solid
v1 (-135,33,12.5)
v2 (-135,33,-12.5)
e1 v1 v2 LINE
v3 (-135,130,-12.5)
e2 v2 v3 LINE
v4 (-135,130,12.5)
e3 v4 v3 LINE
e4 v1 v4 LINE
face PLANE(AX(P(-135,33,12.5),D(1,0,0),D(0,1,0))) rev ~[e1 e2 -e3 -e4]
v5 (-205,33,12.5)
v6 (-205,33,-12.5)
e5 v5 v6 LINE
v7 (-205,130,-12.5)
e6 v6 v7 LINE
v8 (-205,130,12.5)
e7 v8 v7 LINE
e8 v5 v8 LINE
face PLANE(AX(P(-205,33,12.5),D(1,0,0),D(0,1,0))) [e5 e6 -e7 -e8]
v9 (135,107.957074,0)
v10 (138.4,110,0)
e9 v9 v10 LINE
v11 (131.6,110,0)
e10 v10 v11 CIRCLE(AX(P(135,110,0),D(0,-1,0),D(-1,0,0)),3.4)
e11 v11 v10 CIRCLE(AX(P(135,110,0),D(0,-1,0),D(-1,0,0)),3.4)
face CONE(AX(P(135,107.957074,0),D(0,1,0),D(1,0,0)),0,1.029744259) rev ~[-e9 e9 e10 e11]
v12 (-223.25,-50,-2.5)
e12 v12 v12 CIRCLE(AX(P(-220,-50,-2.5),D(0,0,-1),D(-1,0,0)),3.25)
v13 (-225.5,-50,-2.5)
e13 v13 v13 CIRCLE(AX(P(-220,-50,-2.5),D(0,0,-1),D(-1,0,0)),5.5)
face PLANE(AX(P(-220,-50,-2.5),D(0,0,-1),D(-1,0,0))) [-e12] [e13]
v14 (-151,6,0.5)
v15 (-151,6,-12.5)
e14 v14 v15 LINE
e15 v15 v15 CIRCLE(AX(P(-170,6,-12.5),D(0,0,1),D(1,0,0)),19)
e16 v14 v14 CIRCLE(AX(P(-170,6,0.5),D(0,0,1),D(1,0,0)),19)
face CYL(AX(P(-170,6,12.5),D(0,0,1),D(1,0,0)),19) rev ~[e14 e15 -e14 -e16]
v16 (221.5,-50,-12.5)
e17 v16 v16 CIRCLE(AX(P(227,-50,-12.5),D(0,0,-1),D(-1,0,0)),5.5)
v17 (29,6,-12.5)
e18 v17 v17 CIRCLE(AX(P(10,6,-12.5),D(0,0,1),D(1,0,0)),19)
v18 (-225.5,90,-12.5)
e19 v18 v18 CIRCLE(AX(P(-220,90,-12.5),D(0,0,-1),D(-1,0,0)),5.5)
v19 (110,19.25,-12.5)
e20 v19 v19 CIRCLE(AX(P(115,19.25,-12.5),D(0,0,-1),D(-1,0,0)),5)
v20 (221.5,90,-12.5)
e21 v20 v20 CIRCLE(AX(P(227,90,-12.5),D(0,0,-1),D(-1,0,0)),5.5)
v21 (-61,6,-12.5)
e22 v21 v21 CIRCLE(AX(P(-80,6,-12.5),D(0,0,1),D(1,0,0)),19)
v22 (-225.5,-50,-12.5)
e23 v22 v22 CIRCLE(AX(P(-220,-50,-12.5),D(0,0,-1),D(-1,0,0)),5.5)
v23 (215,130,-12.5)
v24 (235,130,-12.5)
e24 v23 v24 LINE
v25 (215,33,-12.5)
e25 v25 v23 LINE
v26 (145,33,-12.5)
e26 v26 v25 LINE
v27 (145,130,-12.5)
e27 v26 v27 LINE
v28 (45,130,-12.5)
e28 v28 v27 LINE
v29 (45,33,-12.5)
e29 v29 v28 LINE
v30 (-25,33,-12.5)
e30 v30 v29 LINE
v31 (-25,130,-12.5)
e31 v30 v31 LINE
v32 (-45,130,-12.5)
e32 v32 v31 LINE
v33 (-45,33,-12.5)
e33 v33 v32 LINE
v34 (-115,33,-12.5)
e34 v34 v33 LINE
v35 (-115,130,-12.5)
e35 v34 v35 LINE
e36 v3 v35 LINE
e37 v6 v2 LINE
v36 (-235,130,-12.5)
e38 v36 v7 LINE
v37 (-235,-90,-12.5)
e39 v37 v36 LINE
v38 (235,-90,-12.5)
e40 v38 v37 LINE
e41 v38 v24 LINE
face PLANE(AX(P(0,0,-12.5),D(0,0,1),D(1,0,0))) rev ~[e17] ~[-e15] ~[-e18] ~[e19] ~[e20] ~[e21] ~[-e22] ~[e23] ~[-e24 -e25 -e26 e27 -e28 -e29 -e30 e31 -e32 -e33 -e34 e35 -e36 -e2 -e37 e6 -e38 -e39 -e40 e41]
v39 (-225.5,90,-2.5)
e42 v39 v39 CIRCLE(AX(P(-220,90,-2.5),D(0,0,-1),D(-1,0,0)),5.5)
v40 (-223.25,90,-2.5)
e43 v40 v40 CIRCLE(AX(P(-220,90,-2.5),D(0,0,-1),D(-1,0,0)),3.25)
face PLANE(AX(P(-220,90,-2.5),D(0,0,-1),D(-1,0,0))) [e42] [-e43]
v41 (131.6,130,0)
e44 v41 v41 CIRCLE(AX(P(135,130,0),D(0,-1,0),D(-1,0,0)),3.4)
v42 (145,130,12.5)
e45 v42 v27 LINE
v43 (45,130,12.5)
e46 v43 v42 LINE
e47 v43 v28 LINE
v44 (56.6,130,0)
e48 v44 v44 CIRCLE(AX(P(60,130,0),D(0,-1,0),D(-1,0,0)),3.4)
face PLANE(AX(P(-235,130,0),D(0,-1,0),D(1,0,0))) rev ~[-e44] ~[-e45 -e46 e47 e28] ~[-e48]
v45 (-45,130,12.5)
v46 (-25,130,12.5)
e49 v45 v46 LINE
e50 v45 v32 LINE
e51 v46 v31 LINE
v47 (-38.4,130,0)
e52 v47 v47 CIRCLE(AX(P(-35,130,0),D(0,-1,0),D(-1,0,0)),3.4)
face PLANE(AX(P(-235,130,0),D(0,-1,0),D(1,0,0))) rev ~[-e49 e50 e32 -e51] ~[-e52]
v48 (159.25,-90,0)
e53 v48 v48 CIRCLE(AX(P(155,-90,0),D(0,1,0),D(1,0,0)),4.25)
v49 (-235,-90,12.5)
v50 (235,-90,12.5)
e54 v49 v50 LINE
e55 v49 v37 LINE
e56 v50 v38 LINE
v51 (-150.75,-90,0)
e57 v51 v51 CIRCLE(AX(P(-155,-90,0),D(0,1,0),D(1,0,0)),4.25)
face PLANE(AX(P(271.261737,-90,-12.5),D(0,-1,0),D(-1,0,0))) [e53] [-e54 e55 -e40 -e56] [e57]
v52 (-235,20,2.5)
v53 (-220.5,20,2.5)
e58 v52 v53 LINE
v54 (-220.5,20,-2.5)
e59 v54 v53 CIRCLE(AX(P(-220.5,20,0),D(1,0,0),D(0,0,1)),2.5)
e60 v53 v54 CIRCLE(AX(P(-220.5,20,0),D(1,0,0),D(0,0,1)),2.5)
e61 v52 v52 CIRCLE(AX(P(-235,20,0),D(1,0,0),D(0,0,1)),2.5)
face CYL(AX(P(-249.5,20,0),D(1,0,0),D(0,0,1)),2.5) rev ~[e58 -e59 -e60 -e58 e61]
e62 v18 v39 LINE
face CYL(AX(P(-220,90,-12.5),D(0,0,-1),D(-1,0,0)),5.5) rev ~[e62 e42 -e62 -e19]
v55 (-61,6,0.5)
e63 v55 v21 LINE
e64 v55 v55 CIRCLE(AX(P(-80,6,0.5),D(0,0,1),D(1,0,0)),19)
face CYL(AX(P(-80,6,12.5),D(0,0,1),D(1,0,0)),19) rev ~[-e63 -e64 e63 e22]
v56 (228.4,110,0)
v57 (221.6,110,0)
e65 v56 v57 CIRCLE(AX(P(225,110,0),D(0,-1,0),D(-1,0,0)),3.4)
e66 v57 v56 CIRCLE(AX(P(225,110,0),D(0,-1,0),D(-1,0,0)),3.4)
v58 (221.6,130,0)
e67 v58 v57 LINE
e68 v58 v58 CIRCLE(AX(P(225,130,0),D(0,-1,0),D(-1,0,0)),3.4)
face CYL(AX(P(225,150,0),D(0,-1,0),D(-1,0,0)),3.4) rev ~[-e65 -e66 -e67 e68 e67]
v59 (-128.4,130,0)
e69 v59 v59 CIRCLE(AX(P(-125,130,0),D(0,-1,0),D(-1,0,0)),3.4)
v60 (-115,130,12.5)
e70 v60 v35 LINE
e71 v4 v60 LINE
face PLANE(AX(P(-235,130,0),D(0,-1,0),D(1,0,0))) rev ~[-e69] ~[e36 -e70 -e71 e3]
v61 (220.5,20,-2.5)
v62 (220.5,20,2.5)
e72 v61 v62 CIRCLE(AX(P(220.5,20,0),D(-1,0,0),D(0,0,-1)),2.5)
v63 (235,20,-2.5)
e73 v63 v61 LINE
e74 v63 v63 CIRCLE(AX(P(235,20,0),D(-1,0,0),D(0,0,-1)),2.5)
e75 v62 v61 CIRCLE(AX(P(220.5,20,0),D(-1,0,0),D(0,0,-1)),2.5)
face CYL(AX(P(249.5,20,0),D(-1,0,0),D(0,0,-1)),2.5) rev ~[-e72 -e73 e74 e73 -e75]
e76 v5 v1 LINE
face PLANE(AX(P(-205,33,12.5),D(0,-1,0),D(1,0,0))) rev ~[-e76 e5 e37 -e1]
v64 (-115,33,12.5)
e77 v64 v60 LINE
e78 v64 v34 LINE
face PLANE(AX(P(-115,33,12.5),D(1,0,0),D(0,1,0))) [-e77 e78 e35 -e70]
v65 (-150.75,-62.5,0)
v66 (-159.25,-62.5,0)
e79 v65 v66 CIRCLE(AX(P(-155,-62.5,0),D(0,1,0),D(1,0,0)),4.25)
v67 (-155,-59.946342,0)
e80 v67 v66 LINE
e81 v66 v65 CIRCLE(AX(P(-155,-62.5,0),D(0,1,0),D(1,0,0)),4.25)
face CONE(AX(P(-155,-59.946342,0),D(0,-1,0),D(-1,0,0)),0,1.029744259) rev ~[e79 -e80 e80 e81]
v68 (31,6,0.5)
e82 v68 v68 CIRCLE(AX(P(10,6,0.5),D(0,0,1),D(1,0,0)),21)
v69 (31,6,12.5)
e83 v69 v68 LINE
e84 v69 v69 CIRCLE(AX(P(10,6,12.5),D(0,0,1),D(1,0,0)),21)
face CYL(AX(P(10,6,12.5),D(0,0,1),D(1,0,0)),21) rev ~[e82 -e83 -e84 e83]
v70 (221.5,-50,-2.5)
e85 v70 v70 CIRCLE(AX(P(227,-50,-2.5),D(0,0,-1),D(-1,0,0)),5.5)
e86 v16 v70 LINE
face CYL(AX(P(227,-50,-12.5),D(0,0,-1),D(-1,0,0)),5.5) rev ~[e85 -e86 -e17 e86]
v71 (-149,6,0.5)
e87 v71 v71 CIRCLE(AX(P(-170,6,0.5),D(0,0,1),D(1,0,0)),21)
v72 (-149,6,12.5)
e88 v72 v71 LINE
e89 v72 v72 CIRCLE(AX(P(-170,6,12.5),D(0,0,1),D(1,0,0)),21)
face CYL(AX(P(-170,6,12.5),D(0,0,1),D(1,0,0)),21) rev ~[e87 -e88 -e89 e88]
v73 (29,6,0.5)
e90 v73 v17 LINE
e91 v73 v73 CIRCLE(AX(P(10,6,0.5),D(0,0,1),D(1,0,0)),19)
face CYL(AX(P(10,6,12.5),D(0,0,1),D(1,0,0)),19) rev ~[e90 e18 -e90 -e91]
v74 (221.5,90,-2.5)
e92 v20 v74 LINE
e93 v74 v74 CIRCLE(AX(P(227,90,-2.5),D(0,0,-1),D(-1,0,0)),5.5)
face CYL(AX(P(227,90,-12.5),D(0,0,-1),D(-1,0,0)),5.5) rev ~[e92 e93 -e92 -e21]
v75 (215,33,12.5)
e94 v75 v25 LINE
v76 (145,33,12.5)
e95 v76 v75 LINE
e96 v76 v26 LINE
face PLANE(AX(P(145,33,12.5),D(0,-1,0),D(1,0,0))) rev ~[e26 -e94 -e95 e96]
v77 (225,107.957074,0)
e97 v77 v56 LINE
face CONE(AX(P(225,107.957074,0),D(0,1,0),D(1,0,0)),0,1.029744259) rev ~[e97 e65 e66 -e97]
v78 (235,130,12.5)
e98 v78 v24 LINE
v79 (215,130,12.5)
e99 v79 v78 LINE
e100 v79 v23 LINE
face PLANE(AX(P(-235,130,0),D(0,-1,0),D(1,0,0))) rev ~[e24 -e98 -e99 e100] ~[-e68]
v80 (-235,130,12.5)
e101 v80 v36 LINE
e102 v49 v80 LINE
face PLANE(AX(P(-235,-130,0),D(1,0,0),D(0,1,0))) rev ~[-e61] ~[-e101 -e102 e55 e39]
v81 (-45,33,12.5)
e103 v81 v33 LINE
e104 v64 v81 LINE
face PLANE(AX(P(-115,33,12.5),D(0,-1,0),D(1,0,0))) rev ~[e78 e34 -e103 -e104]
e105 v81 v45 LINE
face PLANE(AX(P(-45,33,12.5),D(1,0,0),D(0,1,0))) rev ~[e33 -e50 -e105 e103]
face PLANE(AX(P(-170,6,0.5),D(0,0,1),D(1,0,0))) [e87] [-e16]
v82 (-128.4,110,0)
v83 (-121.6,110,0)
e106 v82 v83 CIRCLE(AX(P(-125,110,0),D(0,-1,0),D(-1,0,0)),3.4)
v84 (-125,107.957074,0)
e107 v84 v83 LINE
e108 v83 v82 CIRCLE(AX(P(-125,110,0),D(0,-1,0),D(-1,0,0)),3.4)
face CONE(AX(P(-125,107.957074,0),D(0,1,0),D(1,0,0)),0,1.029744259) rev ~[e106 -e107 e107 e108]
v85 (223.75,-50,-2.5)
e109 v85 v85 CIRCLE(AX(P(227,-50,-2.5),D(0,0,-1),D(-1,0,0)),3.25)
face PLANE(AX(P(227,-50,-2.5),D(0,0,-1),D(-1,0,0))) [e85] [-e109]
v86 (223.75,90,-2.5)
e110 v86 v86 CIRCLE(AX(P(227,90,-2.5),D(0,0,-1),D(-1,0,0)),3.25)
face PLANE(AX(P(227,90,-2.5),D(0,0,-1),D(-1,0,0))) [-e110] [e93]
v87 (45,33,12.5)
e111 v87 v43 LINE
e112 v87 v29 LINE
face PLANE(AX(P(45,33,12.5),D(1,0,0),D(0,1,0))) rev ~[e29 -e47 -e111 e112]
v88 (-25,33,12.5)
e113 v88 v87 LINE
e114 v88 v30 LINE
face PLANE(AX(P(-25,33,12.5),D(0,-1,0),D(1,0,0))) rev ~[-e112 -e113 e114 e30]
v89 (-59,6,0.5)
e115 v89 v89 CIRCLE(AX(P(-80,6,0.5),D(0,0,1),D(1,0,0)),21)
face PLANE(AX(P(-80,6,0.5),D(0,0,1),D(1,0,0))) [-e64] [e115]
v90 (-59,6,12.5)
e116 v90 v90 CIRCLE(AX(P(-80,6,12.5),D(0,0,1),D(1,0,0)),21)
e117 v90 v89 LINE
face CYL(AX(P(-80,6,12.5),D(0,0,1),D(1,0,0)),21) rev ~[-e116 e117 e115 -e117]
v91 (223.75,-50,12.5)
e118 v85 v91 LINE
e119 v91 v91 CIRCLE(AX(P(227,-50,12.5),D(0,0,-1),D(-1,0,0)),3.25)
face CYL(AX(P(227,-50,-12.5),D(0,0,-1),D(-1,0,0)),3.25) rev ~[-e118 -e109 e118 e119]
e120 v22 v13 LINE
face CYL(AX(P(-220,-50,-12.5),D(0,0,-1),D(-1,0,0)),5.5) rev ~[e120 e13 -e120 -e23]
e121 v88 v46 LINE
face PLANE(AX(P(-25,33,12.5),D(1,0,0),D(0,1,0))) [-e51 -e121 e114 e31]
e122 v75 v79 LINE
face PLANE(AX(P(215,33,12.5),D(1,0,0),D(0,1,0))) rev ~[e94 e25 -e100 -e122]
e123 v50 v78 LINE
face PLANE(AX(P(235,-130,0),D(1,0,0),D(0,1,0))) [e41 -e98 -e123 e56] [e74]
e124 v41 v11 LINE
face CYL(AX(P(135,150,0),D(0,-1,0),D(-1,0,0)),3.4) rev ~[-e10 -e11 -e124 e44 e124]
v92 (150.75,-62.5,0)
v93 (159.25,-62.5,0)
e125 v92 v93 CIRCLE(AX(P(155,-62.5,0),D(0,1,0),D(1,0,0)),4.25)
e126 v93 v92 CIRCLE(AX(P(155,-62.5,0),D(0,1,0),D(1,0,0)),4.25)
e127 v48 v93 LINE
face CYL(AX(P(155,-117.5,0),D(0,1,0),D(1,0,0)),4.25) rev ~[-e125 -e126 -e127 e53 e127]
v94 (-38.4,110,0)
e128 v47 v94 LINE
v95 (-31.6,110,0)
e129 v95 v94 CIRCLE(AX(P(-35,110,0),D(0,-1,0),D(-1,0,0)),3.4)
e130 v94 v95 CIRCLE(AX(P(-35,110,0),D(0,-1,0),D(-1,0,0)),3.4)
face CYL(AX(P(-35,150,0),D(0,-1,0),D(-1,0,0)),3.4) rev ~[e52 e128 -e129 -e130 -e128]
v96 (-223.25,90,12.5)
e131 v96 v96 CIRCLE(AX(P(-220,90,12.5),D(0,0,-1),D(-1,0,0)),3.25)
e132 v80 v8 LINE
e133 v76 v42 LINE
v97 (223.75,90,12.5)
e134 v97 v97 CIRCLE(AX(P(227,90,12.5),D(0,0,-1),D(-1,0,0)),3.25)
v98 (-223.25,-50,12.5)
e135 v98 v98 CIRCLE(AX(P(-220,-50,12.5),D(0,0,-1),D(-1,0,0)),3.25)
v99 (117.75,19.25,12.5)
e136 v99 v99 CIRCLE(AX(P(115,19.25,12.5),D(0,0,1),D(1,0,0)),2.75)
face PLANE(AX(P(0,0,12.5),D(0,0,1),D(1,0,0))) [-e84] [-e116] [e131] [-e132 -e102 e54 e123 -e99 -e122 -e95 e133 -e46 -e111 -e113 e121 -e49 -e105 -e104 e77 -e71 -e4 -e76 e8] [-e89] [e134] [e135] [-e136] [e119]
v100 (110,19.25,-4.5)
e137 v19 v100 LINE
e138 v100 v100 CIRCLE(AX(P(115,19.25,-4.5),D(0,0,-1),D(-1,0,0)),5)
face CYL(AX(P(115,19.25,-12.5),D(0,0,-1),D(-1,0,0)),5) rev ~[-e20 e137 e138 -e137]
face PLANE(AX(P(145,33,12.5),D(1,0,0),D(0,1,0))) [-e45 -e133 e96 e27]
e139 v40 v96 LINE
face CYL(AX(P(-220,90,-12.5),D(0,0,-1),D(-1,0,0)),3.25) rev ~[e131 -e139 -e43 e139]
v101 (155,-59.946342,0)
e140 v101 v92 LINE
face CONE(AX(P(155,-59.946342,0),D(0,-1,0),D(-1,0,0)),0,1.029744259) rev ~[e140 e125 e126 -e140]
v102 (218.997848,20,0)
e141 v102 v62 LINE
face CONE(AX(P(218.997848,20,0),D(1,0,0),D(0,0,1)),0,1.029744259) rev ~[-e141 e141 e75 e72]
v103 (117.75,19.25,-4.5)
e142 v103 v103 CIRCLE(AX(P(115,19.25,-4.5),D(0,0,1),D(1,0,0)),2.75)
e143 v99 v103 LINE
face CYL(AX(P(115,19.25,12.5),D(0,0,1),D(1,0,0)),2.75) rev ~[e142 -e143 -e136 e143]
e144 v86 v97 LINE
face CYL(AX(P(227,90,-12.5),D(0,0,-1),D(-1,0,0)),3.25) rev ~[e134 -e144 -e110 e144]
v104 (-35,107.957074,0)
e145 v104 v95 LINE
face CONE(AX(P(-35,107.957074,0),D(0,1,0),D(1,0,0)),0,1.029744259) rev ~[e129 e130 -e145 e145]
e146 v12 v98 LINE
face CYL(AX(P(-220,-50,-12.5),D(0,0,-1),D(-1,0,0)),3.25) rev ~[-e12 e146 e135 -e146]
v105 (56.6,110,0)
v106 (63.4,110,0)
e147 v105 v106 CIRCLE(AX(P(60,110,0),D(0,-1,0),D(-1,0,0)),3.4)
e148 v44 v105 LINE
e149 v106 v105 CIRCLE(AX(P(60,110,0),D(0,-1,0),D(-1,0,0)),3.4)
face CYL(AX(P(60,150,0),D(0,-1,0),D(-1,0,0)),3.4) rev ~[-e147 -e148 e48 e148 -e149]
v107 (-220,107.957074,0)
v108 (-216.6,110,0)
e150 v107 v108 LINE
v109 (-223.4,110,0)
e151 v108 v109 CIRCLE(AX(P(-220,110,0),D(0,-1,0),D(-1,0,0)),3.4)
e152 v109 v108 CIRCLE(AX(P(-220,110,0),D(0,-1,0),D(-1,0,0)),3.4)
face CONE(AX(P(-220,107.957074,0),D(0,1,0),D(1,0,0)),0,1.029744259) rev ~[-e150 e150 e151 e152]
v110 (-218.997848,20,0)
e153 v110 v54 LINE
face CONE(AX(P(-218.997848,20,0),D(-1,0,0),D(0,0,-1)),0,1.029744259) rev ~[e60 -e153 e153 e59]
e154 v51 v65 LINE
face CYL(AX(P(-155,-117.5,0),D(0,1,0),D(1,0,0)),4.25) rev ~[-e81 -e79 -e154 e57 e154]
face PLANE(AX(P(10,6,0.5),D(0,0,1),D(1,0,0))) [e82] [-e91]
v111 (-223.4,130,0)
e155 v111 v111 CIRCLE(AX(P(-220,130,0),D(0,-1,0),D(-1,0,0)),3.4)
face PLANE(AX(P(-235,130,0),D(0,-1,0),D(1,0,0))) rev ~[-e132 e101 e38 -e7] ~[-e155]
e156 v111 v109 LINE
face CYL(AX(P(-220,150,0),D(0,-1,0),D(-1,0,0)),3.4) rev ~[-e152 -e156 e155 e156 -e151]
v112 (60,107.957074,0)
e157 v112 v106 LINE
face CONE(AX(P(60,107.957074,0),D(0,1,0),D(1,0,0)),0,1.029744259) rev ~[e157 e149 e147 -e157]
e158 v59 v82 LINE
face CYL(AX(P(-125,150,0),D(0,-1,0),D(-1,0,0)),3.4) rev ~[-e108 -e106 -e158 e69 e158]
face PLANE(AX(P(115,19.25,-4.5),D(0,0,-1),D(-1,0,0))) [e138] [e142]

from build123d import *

# Parameters (mm, degrees)
SKETCH1_W                       = 470
SKETCH1_H                       = 260
BOSS_EXTRUDE1_DEPTH             = 12.5
SKETCH4_W                       = 70
SKETCH4_H                       = 97
CUT_EXTRUDE3_DEPTH              = 97
SKETCH5_R                       = 2.75
CUT_EXTRUDE4_DEPTH              = 97
SKETCH6_R                       = 5
CUT_EXTRUDE5_DEPTH              = 8
SKETCH7_W                       = 593.529724836
SKETCH7_H                       = 137.698896162
CUT_EXTRUDE6_DEPTH              = 40
M8_TAPPED_HOLE1_D               = 6.8
M8_TAPPED_HOLE1_DEPTH           = 20
M8_TAPPED_HOLE1_TIP             = 2.042926105
M10_TAPPED_HOLE1_D              = 8.5
M10_TAPPED_HOLE1_DEPTH          = 27.5
M10_TAPPED_HOLE1_TIP            = 2.553657631
SKETCH13_R                      = 19
CUT_EXTRUDE7_DEPTH              = 270.722079185
SKETCH14_R                      = 21
CUT_EXTRUDE8_DEPTH              = 12
LPATTERN1_COUNT                 = 3
LPATTERN1_PITCH                 = 90
SKETCH15_R                      = 3.25
CUT_EXTRUDE9_DEPTH              = 270.722079185
SKETCH16_R                      = 5.5
CUT_EXTRUDE10_DEPTH             = 10
LPATTERN2_COUNT                 = 2
LPATTERN2_PITCH                 = 447
M6_TAPPED_HOLE1_D               = 5
M6_TAPPED_HOLE1_DEPTH           = 14.5
M6_TAPPED_HOLE1_TIP             = 1.502151548
M6_TAPPED_HOLE1_ON_FACE_2_D     = 5
M6_TAPPED_HOLE1_ON_FACE_2_DEPTH = 14.5
M6_TAPPED_HOLE1_ON_FACE_2_TIP   = 1.502151548


with BuildPart() as part:
    # Sketch1 → Boss-Extrude1 (new, symmetric)
    with BuildSketch(Plane.XY):
        Rectangle(SKETCH1_W, SKETCH1_H)
    extrude(amount=BOSS_EXTRUDE1_DEPTH, both=True)

    # Sketch4 → Cut-Extrude3 (cut)
    with BuildSketch(Plane.XY.offset(12.5)):
        with Locations((-170, 81.5)):
            Rectangle(SKETCH4_W, SKETCH4_H)
        with Locations((-80, 81.5)):
            Rectangle(SKETCH4_W, SKETCH4_H)
        with Locations((10, 81.5)):
            Rectangle(SKETCH4_W, SKETCH4_H)
        with Locations((180, 81.5)):
            Rectangle(SKETCH4_W, SKETCH4_H)
    extrude(amount=-CUT_EXTRUDE3_DEPTH, mode=Mode.SUBTRACT)

    # Sketch5 → Cut-Extrude4 (cut)
    with BuildSketch(Plane.XY.offset(12.5)):
        with Locations((115, 19.25)):
            Circle(SKETCH5_R)
    extrude(amount=-CUT_EXTRUDE4_DEPTH, mode=Mode.SUBTRACT)

    # Sketch6 → Cut-Extrude5 (cut)
    with BuildSketch(Plane(origin=(0, 0, -12.5), x_dir=(-1, 0, 0), z_dir=(0, 0, -1))):
        with Locations((-115, 19.25)):
            Circle(SKETCH6_R)
    extrude(amount=-CUT_EXTRUDE5_DEPTH, mode=Mode.SUBTRACT)

    # Sketch7 → Cut-Extrude6 (cut)
    with BuildSketch(Plane(origin=(0, 0, -12.5), x_dir=(-1, 0, 0), z_dir=(0, 0, -1))):
        with Locations((25.503124985, -158.849448081)):
            Rectangle(SKETCH7_W, SKETCH7_H)
    extrude(amount=-CUT_EXTRUDE6_DEPTH, mode=Mode.SUBTRACT)

    # M8 Tapped Hole1
    with Locations(Plane(origin=(0, 130, 0), x_dir=(1, 0, 0), z_dir=(0, 1, 0))):
        with Locations((-220, 0), (225, 0), (135, 0), (-35, 0), (-125, 0), (60, 0)):
            Hole(M8_TAPPED_HOLE1_D / 2, depth=M8_TAPPED_HOLE1_DEPTH)
            with Locations((0, 0, -(M8_TAPPED_HOLE1_DEPTH + M8_TAPPED_HOLE1_TIP / 2))):  # 118° drill point
                Cone(0, M8_TAPPED_HOLE1_D / 2, M8_TAPPED_HOLE1_TIP, mode=Mode.SUBTRACT)

    # M10 Tapped Hole1
    with Locations(Plane(origin=(0, -90, 0), x_dir=(-1, 0, 0), z_dir=(0, -1, 0))):
        with Locations((-155, 0), (155, 0)):
            Hole(M10_TAPPED_HOLE1_D / 2, depth=M10_TAPPED_HOLE1_DEPTH)
            with Locations((0, 0, -(M10_TAPPED_HOLE1_DEPTH + M10_TAPPED_HOLE1_TIP / 2))):  # 118° drill point
                Cone(0, M10_TAPPED_HOLE1_D / 2, M10_TAPPED_HOLE1_TIP, mode=Mode.SUBTRACT)

    # Sketch13 → Cut-Extrude7 (cut, through all)
    with BuildSketch(Plane.XY.offset(12.5)):
        with Locations((-170, 6)):
            Circle(SKETCH13_R)
    cut_extrude7 = extrude(amount=-CUT_EXTRUDE7_DEPTH, mode=Mode.SUBTRACT)

    # Sketch14 → Cut-Extrude8 (cut)
    with BuildSketch(Plane.XY.offset(12.5)):
        with Locations((-170, 6)):
            Circle(SKETCH14_R)
    cut_extrude8 = extrude(amount=-CUT_EXTRUDE8_DEPTH, mode=Mode.SUBTRACT)

    # LPattern1: Cut-Extrude7, Cut-Extrude8 ×3
    with Locations(*[(i * LPATTERN1_PITCH, 0, 0) for i in range(1, LPATTERN1_COUNT)]):
        add(cut_extrude7, mode=Mode.SUBTRACT)
        add(cut_extrude8, mode=Mode.SUBTRACT)

    # Sketch15 → Cut-Extrude9 (cut, through all)
    with BuildSketch(Plane(origin=(0, 0, -12.5), x_dir=(-1, 0, 0), z_dir=(0, 0, -1))):
        with Locations((-227, 90)):
            Circle(SKETCH15_R)
        with Locations((-227, -50)):
            Circle(SKETCH15_R)
    cut_extrude9 = extrude(amount=-CUT_EXTRUDE9_DEPTH, mode=Mode.SUBTRACT)

    # Sketch16 → Cut-Extrude10 (cut)
    with BuildSketch(Plane(origin=(0, 0, -12.5), x_dir=(-1, 0, 0), z_dir=(0, 0, -1))):
        with Locations((-227, 90)):
            Circle(SKETCH16_R)
        with Locations((-227, -50)):
            Circle(SKETCH16_R)
    cut_extrude10 = extrude(amount=-CUT_EXTRUDE10_DEPTH, mode=Mode.SUBTRACT)

    # LPattern2: Cut-Extrude9, Cut-Extrude10 ×2
    with Locations(*[(-i * LPATTERN2_PITCH, 0, 0) for i in range(1, LPATTERN2_COUNT)]):
        add(cut_extrude9, mode=Mode.SUBTRACT)
        add(cut_extrude10, mode=Mode.SUBTRACT)

    # M6 Tapped Hole1
    with Locations(Plane(origin=(-235, 20, 0), x_dir=(0, 0, -1), z_dir=(-1, 0, 0))):
        with Locations((0, 0)):
            Hole(M6_TAPPED_HOLE1_D / 2, depth=M6_TAPPED_HOLE1_DEPTH)
            with Locations((0, 0, -(M6_TAPPED_HOLE1_DEPTH + M6_TAPPED_HOLE1_TIP / 2))):  # 118° drill point
                Cone(0, M6_TAPPED_HOLE1_D / 2, M6_TAPPED_HOLE1_TIP, mode=Mode.SUBTRACT)

    # M6 Tapped Hole1 on face 2
    with Locations(Plane(origin=(235, 20, 0), x_dir=(0, 0, 1), z_dir=(1, 0, 0))):
        with Locations((0, 0)):
            Hole(M6_TAPPED_HOLE1_ON_FACE_2_D / 2, depth=M6_TAPPED_HOLE1_ON_FACE_2_DEPTH)
            with Locations((0, 0, -(M6_TAPPED_HOLE1_ON_FACE_2_DEPTH + M6_TAPPED_HOLE1_ON_FACE_2_TIP / 2))):  # 118° drill point
                Cone(0, M6_TAPPED_HOLE1_ON_FACE_2_D / 2, M6_TAPPED_HOLE1_ON_FACE_2_TIP, mode=Mode.SUBTRACT)


solid = part.part
